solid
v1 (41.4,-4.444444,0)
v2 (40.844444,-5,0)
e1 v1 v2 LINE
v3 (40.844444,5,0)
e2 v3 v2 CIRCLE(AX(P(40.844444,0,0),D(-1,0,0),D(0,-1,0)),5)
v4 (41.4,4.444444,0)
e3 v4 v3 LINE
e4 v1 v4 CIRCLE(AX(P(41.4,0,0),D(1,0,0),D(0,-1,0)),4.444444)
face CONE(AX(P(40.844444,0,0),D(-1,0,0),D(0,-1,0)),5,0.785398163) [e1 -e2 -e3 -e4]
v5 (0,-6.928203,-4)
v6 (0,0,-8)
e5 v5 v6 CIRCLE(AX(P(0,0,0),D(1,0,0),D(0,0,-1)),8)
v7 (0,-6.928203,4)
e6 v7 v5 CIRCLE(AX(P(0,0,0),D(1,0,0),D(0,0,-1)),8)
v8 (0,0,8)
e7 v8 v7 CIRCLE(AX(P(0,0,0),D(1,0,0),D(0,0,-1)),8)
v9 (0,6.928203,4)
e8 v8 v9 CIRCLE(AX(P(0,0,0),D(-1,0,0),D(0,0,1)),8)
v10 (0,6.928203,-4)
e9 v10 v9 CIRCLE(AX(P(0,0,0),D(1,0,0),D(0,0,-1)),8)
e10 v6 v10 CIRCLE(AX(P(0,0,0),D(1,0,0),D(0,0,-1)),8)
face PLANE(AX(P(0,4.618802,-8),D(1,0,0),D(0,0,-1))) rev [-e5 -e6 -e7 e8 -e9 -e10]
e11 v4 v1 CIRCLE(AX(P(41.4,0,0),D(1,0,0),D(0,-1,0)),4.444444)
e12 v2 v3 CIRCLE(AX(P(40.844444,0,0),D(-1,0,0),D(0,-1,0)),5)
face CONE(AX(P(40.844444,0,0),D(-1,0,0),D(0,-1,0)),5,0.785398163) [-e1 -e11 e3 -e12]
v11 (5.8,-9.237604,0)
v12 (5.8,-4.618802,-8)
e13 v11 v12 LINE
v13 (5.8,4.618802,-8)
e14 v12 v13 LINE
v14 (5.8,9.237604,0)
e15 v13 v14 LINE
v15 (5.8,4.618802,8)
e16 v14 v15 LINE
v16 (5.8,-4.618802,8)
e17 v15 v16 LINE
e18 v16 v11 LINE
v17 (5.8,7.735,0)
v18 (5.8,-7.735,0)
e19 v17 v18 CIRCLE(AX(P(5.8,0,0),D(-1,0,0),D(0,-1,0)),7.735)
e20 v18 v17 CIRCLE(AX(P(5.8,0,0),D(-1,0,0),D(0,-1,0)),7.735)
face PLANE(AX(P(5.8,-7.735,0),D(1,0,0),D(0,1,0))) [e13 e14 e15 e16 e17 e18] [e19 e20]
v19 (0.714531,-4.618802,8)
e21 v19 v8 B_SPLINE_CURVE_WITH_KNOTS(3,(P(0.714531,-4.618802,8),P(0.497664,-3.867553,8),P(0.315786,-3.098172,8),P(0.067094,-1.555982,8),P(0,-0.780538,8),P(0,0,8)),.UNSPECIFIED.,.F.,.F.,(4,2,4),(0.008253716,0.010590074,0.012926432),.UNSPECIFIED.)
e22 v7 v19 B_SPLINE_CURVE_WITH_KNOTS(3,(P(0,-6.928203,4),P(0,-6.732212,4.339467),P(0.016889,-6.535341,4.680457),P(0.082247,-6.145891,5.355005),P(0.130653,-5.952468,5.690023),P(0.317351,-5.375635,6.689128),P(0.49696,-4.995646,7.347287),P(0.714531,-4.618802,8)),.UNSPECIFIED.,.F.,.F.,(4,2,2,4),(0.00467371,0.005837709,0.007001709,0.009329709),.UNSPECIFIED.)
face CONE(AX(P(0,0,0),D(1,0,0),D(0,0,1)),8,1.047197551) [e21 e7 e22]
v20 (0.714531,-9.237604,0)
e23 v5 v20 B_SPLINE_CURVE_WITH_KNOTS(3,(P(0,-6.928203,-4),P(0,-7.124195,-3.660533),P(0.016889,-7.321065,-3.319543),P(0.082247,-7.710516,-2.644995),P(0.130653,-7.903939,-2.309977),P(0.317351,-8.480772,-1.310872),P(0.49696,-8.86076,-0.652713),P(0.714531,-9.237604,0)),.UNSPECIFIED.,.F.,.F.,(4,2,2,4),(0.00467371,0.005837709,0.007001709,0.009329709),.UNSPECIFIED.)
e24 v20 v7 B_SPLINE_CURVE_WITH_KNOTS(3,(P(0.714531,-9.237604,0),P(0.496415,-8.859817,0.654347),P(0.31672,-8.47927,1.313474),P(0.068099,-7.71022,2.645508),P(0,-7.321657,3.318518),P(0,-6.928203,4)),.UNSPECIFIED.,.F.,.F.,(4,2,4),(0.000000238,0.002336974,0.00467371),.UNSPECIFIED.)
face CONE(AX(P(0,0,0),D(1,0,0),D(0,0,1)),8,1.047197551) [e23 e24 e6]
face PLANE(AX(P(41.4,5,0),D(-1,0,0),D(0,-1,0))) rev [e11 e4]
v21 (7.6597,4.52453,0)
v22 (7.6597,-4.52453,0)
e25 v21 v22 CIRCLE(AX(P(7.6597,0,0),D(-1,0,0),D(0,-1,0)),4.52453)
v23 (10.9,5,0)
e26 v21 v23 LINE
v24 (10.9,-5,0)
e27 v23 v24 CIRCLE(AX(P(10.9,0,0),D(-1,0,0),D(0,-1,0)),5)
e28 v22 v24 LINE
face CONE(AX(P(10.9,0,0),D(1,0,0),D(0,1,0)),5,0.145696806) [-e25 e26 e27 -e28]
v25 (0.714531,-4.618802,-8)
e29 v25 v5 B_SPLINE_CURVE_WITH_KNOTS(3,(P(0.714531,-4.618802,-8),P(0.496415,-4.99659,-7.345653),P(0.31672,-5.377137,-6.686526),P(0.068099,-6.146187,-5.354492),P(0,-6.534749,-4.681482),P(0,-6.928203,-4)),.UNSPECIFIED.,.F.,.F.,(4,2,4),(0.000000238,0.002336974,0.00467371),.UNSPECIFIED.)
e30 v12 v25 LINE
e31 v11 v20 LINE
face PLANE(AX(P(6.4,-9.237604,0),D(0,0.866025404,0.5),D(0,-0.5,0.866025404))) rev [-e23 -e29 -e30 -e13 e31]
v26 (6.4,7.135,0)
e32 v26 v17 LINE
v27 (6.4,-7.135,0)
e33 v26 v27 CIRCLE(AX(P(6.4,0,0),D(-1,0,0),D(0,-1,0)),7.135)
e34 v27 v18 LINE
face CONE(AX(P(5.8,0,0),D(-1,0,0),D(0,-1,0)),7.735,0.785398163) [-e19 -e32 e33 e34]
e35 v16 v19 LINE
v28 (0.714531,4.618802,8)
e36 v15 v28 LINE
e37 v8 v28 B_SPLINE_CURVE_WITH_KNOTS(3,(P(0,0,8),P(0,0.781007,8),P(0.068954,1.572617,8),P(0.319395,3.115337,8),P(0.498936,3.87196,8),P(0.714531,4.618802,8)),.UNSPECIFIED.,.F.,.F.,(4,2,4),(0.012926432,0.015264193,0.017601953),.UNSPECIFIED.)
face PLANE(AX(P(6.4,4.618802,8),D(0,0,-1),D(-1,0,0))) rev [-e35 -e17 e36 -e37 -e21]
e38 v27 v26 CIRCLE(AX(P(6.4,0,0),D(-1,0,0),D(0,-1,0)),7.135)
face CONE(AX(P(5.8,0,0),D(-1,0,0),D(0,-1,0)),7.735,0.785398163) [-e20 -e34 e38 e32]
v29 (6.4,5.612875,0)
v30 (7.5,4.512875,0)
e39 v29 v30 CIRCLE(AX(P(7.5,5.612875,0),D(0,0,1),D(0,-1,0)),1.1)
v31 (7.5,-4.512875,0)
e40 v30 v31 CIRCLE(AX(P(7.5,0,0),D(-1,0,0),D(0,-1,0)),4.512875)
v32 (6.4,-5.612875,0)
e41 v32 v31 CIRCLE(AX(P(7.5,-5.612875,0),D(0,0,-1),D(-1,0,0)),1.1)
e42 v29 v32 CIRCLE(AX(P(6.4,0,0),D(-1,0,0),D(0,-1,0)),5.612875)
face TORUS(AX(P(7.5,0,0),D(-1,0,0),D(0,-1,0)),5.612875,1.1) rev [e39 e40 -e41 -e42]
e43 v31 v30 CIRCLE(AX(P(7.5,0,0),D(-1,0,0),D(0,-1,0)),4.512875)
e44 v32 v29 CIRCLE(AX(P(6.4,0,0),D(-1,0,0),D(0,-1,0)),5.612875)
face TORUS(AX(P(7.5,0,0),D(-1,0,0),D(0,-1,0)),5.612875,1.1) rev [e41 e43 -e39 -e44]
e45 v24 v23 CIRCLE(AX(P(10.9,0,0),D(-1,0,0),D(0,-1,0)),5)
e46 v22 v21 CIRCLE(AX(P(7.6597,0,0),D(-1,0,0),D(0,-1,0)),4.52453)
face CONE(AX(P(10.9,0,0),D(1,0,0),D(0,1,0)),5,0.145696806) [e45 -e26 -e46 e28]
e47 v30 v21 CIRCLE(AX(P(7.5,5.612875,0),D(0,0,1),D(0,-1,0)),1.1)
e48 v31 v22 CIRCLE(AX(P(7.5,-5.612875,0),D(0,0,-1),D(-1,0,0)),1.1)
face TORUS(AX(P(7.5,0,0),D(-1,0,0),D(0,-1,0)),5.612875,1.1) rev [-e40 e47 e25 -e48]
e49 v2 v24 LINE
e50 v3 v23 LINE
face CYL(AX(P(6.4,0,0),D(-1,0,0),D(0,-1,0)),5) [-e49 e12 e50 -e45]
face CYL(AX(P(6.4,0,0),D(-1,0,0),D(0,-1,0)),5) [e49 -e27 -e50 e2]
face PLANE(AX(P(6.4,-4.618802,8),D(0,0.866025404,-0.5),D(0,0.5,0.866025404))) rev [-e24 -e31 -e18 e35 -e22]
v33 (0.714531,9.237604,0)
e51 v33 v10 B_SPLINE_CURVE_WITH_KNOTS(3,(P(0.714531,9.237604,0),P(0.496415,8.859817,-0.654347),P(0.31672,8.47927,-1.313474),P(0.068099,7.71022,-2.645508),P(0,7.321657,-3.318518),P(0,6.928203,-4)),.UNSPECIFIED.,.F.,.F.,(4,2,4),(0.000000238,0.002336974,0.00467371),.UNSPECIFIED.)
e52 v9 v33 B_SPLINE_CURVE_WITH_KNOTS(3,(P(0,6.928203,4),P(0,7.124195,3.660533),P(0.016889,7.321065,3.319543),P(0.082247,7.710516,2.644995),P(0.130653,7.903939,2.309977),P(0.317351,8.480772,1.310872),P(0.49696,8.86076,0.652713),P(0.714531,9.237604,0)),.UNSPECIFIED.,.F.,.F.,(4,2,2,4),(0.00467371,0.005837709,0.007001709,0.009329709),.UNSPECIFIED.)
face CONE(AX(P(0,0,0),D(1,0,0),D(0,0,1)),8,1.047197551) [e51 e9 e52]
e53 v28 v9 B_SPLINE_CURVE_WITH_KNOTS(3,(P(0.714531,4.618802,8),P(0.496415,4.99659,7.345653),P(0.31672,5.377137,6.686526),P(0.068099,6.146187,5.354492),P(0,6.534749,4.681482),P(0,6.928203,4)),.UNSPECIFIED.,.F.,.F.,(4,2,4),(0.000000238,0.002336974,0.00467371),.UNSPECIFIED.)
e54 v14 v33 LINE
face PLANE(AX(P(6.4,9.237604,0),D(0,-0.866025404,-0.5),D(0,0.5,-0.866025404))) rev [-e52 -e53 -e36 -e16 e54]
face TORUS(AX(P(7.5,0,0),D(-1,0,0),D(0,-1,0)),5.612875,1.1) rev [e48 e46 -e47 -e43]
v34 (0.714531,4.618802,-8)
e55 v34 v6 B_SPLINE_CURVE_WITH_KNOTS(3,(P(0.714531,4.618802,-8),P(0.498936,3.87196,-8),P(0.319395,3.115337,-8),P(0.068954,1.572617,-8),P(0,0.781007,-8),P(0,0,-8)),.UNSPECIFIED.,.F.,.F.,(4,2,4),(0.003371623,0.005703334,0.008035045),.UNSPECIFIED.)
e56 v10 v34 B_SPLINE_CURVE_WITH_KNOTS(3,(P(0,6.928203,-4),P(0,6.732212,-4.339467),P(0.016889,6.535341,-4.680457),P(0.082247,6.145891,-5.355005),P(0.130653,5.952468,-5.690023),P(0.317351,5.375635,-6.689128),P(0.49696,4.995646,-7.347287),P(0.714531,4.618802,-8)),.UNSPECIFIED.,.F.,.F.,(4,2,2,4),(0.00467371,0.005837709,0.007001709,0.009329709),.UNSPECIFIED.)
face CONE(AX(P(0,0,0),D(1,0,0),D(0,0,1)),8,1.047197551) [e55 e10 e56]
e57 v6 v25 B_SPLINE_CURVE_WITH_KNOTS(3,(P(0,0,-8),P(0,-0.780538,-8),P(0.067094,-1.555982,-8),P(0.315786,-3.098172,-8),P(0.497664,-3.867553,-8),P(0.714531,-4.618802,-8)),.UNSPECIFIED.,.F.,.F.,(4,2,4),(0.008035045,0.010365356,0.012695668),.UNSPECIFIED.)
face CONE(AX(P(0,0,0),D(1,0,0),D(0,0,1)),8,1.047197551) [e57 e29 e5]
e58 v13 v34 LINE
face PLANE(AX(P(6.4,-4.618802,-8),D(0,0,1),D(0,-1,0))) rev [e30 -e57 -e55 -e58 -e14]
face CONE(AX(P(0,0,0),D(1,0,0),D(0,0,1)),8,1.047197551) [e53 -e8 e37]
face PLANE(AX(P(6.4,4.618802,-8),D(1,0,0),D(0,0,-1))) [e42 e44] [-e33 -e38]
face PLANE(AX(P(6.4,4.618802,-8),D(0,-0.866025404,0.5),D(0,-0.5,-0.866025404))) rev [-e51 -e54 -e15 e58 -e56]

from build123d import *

# Parameters (mm, degrees)
EXTRUDE_1_DEPTH     = 6.4
SKETCH_4_R          = 17.59
SKETCH_4_R_2        = 8
CUT_EXTRUDE_1_DEPTH = 0.8
CUT_EXTRUDE_1_DRAFT = -60
CHAMFER_1_SIZE      = 0.555555556


with BuildPart() as part:
    # 草图3 → 凸台-拉伸1 (new body)
    with BuildSketch(Plane(origin=(0, 0, 0), x_dir=(0, 0, -1), z_dir=(1, 0, 0))):
        Polygon((8, 4.618802154), (0, 9.237604307), (-8, 4.618802154), (-8, -4.618802154), (0, -9.237604307), (8, -4.618802154), align=None)
    extrude(amount=EXTRUDE_1_DEPTH)


with BuildPart() as cut_extrude_1_tool:
    # 草图4 → 切除-拉伸1 (with draft: the straight prism first)
    with BuildSketch(Plane.ZY):
        Circle(SKETCH_4_R)
        Circle(SKETCH_4_R_2, mode=Mode.SUBTRACT)
    extrude(amount=-CUT_EXTRUDE_1_DEPTH)
    # 切除-拉伸1: the draft: its side faces are tilted about the plane it starts from
    cut_extrude_1_sides = [cut_extrude_1_tool.faces().sort_by_distance(p)[0] for p in [
        (0.4, 0, -17.59),
        (0.4, 0, -8),
    ]]
    draft(cut_extrude_1_sides, Plane.ZY, CUT_EXTRUDE_1_DRAFT)


with BuildPart() as part_1:
    add(part.part)

    # 切除-拉伸1: cut by cut_extrude_1_tool
    add(cut_extrude_1_tool.part, mode=Mode.SUBTRACT)

    # 草图6 → 旋转2 (revolve)
    with BuildSketch(Plane.XY, mode=Mode.PRIVATE) as revolve_2_sk:
        with BuildLine():
            Line((10.9, 5), (41.4, 5))
            Line((41.4, 5), (41.4, 0))
            Line((41.4, 0), (6.4, 0))
            Line((6.4, 0), (6.4, 5.612875))
            ThreePointArc((6.4, 5.612875), (6.78085818, 4.780507868), (7.659700078, 4.524529519))
            Line((7.659700078, 4.524529519), (10.9, 5))
        make_face()
    revolve(revolve_2_sk.sketch.rotate(Axis((6.4, 0, 0), (1, 0, 0)), 180), axis=Axis((6.4, 0, 0), (1, 0, 0)))

    # 倒角1
    chamfer_1_edges = [part_1.edges().sort_by_distance(p)[0] for p in [
        (41.4, 5, 0),
    ]]
    chamfer(chamfer_1_edges, length=CHAMFER_1_SIZE)

    # 草图8 → 切除-旋转2 (revolve, cut)
    with BuildSketch(Plane.XY, mode=Mode.PRIVATE) as cut_revolve_2_sk:
        Polygon((6.4, 7.135), (5.8, 7.735), (5.8, 17.59), (6.4, 17.59), align=None)
    revolve(cut_revolve_2_sk.sketch.rotate(Axis((0, 0, 0), (1, 0, 0)), 180), axis=Axis((0, 0, 0), (1, 0, 0)), mode=Mode.SUBTRACT)


solid = part_1.part
